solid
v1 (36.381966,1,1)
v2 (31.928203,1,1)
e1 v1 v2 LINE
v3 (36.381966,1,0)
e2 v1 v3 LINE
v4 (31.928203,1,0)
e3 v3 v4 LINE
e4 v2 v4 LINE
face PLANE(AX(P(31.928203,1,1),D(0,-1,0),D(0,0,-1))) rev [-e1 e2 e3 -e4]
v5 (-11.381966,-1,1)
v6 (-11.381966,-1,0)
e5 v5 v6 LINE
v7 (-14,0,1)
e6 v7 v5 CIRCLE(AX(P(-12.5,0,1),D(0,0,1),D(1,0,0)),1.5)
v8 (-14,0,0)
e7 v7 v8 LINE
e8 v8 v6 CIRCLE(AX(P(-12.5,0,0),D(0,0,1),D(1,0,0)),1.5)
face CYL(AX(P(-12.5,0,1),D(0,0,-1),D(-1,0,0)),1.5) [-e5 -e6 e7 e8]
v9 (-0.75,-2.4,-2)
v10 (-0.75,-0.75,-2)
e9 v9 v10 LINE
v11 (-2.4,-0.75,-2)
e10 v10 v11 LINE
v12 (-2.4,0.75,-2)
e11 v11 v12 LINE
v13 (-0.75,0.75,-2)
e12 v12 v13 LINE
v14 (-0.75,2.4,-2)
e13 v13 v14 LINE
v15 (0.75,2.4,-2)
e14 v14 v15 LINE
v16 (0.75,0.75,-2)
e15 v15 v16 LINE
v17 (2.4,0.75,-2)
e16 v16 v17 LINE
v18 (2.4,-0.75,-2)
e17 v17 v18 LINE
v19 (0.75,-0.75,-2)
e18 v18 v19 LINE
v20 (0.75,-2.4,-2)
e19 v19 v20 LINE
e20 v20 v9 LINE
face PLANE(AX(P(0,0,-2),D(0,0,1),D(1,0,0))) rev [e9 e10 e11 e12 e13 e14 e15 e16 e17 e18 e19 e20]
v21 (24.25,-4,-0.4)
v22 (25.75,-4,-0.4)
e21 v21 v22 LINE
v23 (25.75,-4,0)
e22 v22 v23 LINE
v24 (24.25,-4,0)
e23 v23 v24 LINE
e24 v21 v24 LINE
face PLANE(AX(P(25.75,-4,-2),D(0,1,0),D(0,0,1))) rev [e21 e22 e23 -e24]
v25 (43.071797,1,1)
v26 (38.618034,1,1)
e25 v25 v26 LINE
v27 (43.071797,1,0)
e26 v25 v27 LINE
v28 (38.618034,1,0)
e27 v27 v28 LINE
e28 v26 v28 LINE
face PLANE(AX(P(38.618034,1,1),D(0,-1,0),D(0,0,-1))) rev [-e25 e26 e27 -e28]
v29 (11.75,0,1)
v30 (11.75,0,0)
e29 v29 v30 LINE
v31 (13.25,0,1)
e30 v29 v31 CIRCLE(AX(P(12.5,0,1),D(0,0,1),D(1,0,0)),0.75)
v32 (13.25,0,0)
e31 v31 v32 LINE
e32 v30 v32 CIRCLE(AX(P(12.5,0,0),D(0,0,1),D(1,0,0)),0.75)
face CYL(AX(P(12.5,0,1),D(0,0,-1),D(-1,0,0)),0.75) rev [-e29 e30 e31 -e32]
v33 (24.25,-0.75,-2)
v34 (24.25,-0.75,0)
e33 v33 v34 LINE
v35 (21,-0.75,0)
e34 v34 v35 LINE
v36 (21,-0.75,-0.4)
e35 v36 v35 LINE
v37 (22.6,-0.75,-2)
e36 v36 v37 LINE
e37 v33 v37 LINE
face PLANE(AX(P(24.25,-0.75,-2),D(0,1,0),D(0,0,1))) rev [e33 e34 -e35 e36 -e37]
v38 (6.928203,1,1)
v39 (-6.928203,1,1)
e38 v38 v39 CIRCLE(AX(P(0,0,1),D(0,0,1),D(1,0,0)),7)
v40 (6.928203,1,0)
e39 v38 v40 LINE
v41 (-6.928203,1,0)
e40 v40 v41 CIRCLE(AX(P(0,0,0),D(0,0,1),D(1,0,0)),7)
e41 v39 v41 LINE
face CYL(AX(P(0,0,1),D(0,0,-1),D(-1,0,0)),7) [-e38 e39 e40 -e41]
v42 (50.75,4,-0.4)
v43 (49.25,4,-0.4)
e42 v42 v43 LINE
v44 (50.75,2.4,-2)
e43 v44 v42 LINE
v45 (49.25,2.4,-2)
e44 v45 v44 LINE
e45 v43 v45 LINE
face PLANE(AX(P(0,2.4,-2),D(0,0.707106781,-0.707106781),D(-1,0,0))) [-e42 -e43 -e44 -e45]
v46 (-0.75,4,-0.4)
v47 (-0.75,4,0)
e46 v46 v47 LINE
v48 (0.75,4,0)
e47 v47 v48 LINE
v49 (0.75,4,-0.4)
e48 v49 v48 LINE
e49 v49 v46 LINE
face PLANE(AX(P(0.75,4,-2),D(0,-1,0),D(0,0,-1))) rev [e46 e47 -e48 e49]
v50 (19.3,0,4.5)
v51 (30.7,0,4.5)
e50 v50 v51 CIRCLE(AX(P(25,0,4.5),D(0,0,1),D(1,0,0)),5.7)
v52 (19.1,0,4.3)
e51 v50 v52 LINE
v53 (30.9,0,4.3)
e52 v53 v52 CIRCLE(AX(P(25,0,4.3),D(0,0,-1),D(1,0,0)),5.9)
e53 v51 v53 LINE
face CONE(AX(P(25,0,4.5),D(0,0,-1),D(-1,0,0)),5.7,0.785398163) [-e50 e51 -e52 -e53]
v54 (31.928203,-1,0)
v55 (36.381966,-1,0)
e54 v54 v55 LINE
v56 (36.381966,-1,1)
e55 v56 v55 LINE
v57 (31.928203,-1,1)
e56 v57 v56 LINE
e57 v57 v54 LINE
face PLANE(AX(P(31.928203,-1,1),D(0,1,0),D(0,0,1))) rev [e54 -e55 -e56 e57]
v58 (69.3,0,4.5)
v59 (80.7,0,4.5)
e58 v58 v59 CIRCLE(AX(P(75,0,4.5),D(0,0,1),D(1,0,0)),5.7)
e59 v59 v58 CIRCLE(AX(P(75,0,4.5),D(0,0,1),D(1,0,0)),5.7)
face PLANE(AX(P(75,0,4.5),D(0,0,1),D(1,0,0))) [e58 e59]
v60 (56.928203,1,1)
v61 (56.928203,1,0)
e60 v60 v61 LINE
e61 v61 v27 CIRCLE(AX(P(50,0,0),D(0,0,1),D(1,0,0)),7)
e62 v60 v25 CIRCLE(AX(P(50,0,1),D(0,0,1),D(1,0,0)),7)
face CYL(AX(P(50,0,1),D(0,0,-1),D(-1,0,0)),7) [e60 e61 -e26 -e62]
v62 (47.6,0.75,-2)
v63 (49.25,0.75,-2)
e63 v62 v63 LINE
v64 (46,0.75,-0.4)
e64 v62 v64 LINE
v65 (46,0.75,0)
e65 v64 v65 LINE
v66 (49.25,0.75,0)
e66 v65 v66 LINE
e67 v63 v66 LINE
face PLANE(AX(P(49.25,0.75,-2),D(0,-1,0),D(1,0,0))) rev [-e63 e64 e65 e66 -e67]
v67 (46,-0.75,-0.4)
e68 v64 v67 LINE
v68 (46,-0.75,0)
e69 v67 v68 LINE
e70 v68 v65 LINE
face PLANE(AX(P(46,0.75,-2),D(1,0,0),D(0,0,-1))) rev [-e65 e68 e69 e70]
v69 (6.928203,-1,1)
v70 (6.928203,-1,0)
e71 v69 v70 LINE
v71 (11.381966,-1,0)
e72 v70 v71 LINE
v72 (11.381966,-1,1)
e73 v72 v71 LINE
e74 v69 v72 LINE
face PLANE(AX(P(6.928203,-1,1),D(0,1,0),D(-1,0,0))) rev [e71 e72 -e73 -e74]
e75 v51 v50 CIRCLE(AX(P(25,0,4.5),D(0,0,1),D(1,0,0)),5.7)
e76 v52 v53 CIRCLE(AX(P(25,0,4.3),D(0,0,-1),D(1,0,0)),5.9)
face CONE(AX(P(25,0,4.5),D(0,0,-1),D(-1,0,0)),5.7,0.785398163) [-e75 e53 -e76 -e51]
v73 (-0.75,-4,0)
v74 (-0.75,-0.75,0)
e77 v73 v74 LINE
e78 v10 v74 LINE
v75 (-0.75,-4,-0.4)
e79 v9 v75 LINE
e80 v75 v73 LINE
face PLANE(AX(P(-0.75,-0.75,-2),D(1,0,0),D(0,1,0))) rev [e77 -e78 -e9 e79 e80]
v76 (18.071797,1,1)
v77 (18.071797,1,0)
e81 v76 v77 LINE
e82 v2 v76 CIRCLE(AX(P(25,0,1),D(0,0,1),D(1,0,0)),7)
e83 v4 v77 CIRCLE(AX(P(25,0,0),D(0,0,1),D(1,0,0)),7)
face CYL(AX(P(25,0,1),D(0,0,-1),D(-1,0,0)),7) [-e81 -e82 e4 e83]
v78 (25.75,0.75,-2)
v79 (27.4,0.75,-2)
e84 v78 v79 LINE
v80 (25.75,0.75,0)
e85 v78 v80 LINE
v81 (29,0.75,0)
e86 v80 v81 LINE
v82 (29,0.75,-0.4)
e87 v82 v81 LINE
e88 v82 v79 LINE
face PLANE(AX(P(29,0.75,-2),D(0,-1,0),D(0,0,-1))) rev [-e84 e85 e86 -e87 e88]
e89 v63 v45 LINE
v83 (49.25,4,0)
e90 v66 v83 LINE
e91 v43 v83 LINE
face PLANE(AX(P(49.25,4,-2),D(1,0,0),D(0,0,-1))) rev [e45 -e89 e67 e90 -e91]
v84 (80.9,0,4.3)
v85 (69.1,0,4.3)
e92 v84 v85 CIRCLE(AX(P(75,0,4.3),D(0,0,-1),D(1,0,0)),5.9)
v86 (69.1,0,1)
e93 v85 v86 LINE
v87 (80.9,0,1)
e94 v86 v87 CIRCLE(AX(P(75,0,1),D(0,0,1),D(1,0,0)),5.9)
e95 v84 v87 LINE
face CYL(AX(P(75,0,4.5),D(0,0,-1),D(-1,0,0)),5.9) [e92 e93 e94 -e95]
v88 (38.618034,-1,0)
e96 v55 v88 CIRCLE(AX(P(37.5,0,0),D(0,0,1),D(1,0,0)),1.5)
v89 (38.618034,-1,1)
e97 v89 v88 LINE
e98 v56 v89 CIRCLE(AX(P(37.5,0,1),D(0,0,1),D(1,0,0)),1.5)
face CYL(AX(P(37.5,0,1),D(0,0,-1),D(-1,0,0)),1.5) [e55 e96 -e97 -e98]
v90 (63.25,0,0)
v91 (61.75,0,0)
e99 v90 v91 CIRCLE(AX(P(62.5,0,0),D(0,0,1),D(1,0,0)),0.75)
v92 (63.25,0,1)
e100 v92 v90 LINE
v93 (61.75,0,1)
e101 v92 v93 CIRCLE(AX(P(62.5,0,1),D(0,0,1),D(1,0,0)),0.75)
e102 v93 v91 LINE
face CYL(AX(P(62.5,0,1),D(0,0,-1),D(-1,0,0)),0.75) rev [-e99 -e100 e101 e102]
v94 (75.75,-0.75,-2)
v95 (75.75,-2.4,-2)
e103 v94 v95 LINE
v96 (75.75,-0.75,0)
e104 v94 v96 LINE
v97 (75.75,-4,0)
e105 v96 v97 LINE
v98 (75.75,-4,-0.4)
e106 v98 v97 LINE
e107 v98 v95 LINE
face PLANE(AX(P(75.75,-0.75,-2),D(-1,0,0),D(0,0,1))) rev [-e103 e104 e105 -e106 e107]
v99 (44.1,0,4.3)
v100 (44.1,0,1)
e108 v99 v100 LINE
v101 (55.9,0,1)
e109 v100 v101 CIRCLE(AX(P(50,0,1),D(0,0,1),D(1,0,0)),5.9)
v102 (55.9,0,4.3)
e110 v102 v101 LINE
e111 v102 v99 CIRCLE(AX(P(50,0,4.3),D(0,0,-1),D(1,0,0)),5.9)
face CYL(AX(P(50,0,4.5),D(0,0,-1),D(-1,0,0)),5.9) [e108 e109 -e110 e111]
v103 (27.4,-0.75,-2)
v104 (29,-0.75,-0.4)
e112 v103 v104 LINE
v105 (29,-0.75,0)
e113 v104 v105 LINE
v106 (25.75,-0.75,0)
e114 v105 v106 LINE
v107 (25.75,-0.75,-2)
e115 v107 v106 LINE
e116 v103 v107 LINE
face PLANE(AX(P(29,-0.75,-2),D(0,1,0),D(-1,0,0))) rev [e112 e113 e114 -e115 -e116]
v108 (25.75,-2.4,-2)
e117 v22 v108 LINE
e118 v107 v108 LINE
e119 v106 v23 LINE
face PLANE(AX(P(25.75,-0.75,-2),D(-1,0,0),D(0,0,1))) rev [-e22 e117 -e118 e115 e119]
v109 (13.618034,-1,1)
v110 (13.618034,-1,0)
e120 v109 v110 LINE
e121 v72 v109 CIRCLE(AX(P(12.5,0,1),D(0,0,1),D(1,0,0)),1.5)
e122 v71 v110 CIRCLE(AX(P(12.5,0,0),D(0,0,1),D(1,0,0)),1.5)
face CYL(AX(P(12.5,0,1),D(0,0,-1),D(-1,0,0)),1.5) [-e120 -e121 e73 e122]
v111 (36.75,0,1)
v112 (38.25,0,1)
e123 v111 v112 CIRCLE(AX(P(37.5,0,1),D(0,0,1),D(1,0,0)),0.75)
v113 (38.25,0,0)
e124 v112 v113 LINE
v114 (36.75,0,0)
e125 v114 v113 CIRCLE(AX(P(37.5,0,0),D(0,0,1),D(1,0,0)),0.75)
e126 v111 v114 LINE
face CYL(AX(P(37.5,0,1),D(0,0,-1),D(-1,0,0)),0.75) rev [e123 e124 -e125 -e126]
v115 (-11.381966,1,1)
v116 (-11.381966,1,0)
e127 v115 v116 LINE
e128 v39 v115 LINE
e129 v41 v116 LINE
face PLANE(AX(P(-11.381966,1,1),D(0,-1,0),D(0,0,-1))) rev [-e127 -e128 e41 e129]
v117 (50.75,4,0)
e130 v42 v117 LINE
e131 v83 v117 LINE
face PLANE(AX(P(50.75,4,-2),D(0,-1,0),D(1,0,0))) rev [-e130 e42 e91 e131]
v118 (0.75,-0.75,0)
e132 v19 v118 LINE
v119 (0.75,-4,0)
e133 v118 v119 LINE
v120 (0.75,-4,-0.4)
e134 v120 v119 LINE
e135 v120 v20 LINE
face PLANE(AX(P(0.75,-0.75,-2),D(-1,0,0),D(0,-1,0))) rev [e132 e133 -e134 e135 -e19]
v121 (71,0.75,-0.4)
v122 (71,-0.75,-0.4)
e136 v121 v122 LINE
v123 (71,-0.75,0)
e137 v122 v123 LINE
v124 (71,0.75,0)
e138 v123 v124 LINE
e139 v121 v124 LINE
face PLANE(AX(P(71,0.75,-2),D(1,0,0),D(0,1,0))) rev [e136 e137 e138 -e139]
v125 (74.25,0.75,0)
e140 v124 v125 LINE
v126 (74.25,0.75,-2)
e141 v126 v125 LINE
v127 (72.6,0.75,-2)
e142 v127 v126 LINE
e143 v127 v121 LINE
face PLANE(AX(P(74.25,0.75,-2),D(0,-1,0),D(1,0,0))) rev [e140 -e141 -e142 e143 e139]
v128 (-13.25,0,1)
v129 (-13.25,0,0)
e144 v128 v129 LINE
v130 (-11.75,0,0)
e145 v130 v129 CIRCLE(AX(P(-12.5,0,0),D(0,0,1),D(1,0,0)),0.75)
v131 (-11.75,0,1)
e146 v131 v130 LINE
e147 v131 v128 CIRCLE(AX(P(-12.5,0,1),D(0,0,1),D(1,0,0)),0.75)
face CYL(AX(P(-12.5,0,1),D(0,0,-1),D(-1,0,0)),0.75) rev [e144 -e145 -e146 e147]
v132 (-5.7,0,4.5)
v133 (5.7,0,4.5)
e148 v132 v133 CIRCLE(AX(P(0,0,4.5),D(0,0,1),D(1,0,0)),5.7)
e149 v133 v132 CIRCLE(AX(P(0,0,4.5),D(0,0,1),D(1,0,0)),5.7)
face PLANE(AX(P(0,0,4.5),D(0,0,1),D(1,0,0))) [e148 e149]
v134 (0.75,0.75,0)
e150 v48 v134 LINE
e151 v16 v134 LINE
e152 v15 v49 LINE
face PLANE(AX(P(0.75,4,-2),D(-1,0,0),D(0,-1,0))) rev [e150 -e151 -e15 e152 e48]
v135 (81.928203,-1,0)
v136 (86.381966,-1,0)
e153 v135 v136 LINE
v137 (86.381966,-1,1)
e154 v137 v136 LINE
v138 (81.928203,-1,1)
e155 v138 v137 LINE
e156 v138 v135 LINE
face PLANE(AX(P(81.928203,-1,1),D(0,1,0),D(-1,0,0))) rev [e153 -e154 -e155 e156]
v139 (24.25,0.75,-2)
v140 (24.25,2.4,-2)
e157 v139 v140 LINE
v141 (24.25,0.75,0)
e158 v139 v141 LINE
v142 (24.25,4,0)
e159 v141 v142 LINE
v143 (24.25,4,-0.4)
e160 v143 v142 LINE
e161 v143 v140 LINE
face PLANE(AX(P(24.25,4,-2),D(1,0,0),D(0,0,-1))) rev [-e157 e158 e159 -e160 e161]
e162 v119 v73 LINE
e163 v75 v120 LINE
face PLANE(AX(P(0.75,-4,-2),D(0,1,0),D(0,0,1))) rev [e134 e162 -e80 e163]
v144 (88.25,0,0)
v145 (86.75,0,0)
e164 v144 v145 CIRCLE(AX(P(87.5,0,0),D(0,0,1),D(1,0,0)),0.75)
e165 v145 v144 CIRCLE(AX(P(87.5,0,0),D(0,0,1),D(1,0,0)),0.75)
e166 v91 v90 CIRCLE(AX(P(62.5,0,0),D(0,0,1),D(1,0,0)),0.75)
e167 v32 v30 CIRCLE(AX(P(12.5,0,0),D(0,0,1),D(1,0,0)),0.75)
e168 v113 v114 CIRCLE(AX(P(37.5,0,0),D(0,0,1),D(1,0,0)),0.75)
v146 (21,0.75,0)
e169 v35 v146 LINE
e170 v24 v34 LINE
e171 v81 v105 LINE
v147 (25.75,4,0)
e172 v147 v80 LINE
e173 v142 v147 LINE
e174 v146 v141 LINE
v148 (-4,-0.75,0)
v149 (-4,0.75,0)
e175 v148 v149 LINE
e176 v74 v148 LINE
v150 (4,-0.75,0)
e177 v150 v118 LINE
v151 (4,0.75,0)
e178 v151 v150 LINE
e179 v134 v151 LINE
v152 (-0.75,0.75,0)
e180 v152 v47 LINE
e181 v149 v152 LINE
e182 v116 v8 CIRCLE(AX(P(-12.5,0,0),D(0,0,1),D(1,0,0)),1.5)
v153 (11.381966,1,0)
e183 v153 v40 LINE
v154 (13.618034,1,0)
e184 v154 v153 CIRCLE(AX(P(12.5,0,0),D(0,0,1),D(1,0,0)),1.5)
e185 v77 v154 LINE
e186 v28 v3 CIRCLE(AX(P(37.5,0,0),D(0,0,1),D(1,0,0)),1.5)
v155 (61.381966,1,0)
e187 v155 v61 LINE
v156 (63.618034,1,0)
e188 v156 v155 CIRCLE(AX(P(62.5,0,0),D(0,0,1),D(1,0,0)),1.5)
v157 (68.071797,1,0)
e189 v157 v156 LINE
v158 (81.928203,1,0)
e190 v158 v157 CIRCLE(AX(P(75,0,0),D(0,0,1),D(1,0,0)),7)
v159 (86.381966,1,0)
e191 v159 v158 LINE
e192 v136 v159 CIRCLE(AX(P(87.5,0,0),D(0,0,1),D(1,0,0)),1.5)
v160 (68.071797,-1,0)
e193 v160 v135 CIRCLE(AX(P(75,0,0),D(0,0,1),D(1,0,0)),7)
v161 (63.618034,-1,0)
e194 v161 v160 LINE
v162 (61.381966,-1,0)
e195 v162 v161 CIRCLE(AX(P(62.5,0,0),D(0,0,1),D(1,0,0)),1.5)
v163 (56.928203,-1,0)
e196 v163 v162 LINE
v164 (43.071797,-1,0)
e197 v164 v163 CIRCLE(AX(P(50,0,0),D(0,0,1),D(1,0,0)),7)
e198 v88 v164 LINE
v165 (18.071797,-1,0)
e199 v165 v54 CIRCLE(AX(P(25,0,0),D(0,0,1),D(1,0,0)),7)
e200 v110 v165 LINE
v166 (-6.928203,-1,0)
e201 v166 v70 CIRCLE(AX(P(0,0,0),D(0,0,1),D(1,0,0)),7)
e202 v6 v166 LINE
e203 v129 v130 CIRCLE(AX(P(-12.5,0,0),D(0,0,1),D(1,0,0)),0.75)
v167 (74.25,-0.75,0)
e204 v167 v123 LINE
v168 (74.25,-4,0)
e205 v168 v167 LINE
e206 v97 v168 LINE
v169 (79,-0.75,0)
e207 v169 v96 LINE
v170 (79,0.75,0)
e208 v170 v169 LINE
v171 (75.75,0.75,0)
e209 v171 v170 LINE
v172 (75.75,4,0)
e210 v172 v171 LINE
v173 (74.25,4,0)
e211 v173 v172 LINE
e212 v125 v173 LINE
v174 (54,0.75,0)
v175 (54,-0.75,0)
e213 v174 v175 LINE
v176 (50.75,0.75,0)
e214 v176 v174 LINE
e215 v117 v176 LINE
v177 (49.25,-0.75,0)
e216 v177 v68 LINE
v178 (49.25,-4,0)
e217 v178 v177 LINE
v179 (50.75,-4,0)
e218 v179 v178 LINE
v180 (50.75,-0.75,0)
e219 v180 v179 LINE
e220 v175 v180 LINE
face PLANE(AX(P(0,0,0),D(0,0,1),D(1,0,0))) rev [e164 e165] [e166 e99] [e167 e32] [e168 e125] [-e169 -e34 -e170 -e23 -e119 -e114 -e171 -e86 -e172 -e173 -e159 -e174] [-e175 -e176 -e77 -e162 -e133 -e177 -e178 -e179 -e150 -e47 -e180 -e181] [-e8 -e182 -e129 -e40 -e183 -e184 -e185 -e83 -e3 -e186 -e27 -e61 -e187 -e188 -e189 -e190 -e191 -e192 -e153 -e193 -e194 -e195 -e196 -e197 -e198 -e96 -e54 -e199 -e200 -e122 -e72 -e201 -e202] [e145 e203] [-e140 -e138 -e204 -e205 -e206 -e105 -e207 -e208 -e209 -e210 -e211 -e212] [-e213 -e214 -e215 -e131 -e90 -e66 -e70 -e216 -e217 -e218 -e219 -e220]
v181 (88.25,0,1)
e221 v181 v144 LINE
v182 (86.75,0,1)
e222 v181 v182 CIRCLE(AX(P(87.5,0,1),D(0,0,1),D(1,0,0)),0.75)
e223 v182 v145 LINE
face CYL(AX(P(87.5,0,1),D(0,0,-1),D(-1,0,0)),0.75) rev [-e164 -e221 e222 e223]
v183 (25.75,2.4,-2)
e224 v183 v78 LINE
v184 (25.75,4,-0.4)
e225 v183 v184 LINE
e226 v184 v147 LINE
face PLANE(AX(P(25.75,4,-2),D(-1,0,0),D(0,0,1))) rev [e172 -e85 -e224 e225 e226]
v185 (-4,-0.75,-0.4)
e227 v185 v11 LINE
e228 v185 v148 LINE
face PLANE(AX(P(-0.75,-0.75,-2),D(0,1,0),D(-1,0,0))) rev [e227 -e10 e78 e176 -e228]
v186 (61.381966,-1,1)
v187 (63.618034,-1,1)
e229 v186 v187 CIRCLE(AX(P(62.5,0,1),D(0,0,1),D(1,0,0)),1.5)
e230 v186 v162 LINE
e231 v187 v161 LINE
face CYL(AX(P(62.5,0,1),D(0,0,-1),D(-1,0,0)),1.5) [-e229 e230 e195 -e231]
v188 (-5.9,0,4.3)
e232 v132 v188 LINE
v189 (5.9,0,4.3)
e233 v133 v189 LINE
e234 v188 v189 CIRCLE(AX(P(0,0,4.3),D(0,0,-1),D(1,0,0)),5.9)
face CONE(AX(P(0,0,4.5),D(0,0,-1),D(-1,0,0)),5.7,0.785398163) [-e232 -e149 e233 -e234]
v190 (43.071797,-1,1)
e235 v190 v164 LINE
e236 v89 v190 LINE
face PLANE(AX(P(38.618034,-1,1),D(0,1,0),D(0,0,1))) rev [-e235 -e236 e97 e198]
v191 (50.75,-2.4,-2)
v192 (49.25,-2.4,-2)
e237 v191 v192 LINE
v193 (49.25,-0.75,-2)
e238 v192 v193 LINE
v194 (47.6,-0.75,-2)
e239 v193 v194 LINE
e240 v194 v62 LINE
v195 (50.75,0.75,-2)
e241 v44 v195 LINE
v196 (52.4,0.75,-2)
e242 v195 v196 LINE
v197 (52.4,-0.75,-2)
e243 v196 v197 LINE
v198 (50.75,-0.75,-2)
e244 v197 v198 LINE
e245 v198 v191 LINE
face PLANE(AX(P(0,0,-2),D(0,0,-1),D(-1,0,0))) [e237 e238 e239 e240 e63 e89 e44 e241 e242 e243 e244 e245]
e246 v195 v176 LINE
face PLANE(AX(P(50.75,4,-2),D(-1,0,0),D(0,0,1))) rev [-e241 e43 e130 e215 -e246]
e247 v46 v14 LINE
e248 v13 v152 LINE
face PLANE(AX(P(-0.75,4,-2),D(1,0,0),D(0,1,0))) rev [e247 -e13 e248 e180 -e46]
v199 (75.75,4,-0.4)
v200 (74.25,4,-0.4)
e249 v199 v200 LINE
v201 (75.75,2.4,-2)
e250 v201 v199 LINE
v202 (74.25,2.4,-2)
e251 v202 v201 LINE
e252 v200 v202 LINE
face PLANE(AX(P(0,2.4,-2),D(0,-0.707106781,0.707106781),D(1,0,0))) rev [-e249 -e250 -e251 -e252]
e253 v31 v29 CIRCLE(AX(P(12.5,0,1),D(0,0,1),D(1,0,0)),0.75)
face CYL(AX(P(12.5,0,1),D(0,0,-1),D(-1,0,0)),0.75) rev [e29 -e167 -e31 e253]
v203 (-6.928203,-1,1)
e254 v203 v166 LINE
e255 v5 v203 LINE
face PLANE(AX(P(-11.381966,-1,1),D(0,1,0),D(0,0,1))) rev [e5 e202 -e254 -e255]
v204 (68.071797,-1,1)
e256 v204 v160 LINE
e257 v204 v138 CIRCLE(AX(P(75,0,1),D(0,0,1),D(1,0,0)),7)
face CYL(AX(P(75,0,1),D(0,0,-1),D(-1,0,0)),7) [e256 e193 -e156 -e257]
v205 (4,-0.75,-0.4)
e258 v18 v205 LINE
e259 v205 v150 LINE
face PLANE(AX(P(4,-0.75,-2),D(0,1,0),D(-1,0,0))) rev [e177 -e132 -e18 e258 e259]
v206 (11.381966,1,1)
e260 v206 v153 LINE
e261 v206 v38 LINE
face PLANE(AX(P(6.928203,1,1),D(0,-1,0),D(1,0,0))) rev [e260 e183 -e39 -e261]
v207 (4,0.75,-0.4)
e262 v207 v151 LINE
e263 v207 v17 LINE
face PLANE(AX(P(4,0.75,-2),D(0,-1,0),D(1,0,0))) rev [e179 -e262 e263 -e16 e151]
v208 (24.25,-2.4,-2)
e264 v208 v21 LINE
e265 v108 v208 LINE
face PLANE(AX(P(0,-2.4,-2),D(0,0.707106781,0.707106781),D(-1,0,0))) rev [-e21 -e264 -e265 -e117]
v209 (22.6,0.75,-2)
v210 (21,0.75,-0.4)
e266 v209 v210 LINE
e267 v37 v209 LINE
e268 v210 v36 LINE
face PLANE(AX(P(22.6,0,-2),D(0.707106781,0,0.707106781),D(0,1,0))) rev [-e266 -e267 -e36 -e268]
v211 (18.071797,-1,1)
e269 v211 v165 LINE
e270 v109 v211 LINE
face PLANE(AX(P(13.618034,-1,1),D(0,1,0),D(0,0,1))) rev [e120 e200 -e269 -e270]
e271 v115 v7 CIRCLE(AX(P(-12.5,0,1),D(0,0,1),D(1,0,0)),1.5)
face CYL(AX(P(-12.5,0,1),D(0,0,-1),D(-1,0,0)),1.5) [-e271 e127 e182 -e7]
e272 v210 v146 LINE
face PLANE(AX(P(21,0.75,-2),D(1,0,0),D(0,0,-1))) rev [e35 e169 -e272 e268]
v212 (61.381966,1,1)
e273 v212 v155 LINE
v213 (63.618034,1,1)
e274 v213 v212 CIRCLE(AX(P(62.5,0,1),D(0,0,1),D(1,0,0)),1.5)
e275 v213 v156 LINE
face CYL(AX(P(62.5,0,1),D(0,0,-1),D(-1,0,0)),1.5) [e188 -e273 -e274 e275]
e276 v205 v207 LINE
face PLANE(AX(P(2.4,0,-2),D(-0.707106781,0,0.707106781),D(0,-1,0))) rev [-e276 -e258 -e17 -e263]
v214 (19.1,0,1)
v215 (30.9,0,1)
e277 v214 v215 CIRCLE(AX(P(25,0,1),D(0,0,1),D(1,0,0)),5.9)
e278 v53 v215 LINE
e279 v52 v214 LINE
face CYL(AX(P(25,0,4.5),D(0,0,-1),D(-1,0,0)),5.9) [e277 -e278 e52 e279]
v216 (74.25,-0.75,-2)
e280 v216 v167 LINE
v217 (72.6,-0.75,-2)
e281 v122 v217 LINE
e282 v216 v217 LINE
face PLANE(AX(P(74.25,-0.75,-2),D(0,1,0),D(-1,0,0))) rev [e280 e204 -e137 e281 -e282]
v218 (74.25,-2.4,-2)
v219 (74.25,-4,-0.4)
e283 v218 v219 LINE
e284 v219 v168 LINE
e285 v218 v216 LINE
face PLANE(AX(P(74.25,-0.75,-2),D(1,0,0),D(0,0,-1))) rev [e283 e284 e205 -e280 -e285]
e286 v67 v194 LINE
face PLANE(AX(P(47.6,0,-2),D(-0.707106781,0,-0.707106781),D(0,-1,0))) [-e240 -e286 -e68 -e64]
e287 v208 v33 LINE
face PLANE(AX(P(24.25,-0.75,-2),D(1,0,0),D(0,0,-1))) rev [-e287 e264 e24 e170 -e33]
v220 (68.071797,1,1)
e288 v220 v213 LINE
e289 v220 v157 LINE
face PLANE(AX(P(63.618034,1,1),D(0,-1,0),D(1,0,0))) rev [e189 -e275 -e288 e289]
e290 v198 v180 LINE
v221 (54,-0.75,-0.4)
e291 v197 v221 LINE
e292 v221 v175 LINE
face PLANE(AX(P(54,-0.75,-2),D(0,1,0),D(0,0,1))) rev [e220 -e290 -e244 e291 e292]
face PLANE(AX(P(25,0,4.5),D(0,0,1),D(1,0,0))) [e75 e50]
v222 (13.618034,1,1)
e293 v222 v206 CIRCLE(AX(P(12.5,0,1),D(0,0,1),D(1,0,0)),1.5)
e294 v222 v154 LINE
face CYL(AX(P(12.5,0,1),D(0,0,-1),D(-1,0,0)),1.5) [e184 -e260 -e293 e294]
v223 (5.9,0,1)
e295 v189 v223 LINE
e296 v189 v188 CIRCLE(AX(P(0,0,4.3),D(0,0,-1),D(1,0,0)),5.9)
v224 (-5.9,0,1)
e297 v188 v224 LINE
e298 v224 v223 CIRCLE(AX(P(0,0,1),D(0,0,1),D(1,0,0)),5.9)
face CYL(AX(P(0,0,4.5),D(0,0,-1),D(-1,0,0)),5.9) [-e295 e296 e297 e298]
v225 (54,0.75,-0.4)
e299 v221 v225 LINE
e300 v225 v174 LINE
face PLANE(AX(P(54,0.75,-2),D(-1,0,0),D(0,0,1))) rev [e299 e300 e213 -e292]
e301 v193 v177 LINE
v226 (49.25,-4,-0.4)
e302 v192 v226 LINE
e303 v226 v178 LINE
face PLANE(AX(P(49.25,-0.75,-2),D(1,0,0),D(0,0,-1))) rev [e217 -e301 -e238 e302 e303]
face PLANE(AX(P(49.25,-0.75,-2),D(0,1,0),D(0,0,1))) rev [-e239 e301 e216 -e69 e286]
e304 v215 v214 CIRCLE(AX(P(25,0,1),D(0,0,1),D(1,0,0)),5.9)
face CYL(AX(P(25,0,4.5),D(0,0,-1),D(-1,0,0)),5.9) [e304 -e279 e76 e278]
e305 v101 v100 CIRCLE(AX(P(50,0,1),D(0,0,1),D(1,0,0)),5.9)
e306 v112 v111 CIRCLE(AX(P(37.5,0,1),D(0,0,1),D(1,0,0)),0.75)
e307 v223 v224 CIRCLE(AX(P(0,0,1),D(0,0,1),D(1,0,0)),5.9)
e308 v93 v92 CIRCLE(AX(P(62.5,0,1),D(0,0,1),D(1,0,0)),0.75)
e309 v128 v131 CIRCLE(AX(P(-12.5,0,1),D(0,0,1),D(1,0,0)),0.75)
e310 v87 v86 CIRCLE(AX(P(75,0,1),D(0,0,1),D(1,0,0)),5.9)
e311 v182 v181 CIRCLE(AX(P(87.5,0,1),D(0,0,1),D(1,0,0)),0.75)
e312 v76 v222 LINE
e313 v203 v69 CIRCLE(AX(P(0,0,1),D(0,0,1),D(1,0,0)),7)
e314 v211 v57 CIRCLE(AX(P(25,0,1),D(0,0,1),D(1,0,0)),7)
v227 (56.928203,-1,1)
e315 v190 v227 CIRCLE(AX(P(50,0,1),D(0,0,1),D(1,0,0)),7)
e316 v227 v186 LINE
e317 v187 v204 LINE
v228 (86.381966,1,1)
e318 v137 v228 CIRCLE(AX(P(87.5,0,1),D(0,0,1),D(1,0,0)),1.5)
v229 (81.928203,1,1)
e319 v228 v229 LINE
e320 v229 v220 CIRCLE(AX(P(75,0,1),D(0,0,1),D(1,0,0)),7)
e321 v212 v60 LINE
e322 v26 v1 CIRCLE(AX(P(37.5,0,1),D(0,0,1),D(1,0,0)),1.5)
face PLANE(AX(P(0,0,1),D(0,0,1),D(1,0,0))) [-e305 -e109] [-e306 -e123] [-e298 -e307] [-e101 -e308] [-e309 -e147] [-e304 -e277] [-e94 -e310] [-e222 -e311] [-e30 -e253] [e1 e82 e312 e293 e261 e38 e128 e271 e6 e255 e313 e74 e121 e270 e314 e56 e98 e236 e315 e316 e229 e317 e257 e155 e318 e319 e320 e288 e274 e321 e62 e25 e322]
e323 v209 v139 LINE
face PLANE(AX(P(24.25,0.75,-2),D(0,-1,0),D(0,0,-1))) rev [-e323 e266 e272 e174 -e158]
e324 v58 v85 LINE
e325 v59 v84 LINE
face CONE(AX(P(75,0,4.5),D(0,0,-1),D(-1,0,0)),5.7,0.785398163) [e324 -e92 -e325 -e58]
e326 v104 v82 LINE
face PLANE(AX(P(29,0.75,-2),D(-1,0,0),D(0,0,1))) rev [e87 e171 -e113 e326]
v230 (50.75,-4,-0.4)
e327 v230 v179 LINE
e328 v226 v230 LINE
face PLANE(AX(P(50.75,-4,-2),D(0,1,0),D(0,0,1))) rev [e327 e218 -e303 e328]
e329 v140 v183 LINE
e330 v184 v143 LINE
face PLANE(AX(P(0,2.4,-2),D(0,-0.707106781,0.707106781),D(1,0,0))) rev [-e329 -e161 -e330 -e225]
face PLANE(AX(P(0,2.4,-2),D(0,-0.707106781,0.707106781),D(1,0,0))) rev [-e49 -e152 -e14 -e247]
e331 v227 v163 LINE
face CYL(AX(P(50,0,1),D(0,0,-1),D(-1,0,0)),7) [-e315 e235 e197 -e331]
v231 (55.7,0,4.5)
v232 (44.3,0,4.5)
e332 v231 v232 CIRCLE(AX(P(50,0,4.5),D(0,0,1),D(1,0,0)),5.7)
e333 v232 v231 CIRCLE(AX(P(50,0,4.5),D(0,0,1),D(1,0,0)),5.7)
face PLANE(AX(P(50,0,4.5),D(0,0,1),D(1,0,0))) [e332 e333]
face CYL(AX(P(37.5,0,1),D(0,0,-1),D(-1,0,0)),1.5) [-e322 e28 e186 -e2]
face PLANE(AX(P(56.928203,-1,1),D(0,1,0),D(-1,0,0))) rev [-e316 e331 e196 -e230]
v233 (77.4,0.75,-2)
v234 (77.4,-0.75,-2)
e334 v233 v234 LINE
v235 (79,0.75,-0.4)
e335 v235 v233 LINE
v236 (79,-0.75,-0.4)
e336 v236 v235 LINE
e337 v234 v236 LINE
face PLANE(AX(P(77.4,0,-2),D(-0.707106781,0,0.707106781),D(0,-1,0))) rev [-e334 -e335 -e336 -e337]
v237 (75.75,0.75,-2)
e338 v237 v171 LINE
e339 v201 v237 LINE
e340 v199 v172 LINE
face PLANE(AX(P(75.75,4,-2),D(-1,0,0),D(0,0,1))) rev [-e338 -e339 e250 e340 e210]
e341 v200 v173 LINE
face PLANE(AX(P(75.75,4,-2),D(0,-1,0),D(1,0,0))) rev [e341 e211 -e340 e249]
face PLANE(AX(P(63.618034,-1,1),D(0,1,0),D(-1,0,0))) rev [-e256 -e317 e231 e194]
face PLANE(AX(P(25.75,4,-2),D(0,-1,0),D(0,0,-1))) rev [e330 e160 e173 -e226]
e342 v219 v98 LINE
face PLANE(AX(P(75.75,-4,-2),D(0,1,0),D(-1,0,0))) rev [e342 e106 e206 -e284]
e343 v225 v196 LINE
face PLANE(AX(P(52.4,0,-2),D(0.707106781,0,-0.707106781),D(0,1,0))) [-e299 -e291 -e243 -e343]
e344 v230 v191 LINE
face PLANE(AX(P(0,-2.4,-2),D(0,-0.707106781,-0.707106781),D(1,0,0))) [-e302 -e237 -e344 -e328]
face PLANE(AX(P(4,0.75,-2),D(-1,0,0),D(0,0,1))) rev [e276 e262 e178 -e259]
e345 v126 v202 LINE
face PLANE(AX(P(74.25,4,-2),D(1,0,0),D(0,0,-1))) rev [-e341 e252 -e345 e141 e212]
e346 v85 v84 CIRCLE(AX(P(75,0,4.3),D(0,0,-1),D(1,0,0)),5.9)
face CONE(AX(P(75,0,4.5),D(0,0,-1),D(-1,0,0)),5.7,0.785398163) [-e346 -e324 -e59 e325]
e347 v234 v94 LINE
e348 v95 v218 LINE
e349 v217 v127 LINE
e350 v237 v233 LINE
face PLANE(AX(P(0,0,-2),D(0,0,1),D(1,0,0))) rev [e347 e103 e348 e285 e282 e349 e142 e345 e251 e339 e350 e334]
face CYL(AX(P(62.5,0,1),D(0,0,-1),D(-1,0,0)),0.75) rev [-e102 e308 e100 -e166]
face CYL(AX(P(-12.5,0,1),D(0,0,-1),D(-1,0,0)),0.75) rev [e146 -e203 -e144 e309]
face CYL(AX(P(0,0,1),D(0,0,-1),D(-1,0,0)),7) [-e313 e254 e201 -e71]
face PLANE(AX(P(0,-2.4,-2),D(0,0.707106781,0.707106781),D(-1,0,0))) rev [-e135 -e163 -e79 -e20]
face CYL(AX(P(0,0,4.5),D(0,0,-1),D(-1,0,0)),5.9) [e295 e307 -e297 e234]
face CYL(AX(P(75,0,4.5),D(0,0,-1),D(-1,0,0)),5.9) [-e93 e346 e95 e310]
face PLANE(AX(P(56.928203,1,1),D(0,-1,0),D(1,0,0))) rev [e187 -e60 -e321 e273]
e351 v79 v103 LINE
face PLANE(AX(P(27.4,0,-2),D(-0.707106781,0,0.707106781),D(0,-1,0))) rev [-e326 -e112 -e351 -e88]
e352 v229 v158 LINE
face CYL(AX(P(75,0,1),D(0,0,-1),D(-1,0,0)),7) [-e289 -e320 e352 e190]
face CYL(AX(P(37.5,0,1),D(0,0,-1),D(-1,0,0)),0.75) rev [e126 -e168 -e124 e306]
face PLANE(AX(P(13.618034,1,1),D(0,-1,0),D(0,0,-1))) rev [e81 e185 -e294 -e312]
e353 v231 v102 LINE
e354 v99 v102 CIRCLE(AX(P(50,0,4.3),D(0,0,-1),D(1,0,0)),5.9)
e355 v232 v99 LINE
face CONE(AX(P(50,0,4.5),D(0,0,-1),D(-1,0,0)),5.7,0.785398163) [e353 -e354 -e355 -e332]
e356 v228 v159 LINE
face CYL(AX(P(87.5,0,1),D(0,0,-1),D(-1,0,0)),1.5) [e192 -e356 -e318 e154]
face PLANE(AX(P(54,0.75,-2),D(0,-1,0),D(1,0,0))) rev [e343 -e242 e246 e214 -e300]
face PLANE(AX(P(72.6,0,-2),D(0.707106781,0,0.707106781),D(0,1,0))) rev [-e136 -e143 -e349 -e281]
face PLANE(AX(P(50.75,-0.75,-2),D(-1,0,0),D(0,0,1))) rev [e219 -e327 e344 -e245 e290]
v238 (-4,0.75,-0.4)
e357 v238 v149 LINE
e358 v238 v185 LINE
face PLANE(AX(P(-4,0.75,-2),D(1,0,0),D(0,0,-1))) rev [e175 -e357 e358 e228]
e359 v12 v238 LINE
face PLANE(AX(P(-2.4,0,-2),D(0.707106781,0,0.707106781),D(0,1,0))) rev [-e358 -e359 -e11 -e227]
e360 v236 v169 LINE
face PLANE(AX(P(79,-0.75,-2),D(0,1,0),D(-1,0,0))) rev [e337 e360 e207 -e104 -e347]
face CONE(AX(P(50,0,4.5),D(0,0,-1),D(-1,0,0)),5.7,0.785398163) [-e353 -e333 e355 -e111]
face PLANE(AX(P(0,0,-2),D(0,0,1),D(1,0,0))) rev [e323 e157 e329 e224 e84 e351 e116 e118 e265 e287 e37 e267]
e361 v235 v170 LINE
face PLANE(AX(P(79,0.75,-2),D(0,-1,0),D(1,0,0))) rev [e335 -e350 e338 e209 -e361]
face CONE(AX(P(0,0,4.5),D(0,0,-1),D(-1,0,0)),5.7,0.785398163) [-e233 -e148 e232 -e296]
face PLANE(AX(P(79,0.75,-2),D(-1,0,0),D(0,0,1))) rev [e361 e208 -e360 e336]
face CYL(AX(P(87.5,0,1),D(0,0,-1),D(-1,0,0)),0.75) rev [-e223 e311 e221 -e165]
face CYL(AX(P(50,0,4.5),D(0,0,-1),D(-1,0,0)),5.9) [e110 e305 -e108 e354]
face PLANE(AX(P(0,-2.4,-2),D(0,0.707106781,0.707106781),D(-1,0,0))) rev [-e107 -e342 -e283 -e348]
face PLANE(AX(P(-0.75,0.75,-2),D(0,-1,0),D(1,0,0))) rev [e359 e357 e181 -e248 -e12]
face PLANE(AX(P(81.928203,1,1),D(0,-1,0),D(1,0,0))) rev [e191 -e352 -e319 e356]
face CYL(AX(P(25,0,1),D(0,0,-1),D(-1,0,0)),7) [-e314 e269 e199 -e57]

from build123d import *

# Parameters (mm, degrees)
SKETCH1_R           = 0.75
BOSS_EXTRUDE1_DEPTH = 1
SKETCH2_R           = 5.9
BOSS_EXTRUDE2_DEPTH = 3.5
CHAMFER1_SIZE       = 0.2
BOSS_EXTRUDE3_DEPTH = 2
CHAMFER2_SIZE       = 1.6


with BuildPart() as part:
    # Sketch1 → Boss-Extrude1 (new body)
    with BuildSketch(Plane.XY):
        with BuildLine():
            Line((-11.381966011, 1), (-6.92820323, 1))
            ThreePointArc((-6.92820323, 1), (0, 7), (6.92820323, 1))
            Line((6.92820323, 1), (11.381966011, 1))
            ThreePointArc((11.381966011, 1), (12.5, 1.5), (13.618033989, 1))
            Line((13.618033989, 1), (18.07179677, 1))
            ThreePointArc((18.07179677, 1), (25, 7), (31.92820323, 1))
            Line((31.92820323, 1), (36.381966011, 1))
            ThreePointArc((36.381966011, 1), (37.5, 1.5), (38.618033989, 1))
            Line((38.618033989, 1), (43.07179677, 1))
            ThreePointArc((43.07179677, 1), (50, 7), (56.92820323, 1))
            Line((56.92820323, 1), (61.381966011, 1))
            ThreePointArc((61.381966011, 1), (62.5, 1.5), (63.618033989, 1))
            Line((63.618033989, 1), (68.07179677, 1))
            ThreePointArc((68.07179677, 1), (75, 7), (81.92820323, 1))
            Line((81.92820323, 1), (86.381966011, 1))
            ThreePointArc((86.381966011, 1), (89, 0), (86.381966011, -1))
            Line((86.381966011, -1), (81.92820323, -1))
            ThreePointArc((81.92820323, -1), (75, -7), (68.07179677, -1))
            Line((68.07179677, -1), (63.618033989, -1))
            ThreePointArc((63.618033989, -1), (62.5, -1.5), (61.381966011, -1))
            Line((61.381966011, -1), (56.92820323, -1))
            ThreePointArc((56.92820323, -1), (50, -7), (43.07179677, -1))
            Line((43.07179677, -1), (38.618033989, -1))
            ThreePointArc((38.618033989, -1), (37.5, -1.5), (36.381966011, -1))
            Line((36.381966011, -1), (31.92820323, -1))
            ThreePointArc((31.92820323, -1), (25, -7), (18.07179677, -1))
            Line((18.07179677, -1), (13.618033989, -1))
            ThreePointArc((13.618033989, -1), (12.5, -1.5), (11.381966011, -1))
            Line((11.381966011, -1), (6.92820323, -1))
            ThreePointArc((6.92820323, -1), (0, -7), (-6.92820323, -1))
            Line((-6.92820323, -1), (-11.381966011, -1))
            ThreePointArc((-11.381966011, -1), (-14, 0), (-11.381966011, 1))
        make_face()
        with Locations((12.5, 0)):
            Circle(SKETCH1_R, mode=Mode.SUBTRACT)
        with Locations((37.5, 0)):
            Circle(SKETCH1_R, mode=Mode.SUBTRACT)
        with Locations((62.5, 0)):
            Circle(SKETCH1_R, mode=Mode.SUBTRACT)
        with Locations((-12.5, 0)):
            Circle(SKETCH1_R, mode=Mode.SUBTRACT)
        with Locations((87.5, 0)):
            Circle(SKETCH1_R, mode=Mode.SUBTRACT)
    extrude(amount=BOSS_EXTRUDE1_DEPTH)

    # Sketch2 → Boss-Extrude2 (add)
    with BuildSketch(Plane.XY.offset(1)):
        Circle(SKETCH2_R)
        with Locations((25, 0)):
            Circle(SKETCH2_R)
        with Locations((50, 0)):
            Circle(SKETCH2_R)
        with Locations((75, 0)):
            Circle(SKETCH2_R)
    extrude(amount=BOSS_EXTRUDE2_DEPTH)

    # Chamfer1
    chamfer1_edges = [part.edges().sort_by_distance(p)[0] for p in [
        (-5.9, 0, 4.5),
        (19.1, 0, 4.5),
        (44.1, 0, 4.5),
        (69.1, 0, 4.5),
    ]]
    chamfer(chamfer1_edges, length=CHAMFER1_SIZE)

    # Sketch3 → Boss-Extrude3 (add)
    with BuildSketch(Plane(origin=(0, 0, 0), x_dir=(-1, 0, 0), z_dir=(0, 0, -1))):
        Polygon((-74.25, -0.75), (-74.25, -4), (-75.75, -4), (-75.75, -0.75), (-79, -0.75), (-79, 0.75), (-75.75, 0.75), (-75.75, 4), (-74.25, 4), (-74.25, 0.75), (-71, 0.75), (-71, -0.75), align=None)
        Polygon((-50.75, 4), (-49.25, 4), (-49.25, 0.75), (-46, 0.75), (-46, -0.75), (-49.25, -0.75), (-49.25, -4), (-50.75, -4), (-50.75, -0.75), (-54, -0.75), (-54, 0.75), (-50.75, 0.75), align=None)
        Polygon((-29, 0.75), (-25.75, 0.75), (-25.75, 4), (-24.25, 4), (-24.25, 0.75), (-21, 0.75), (-21, -0.75), (-24.25, -0.75), (-24.25, -4), (-25.75, -4), (-25.75, -0.75), (-29, -0.75), align=None)
        Polygon((-4, 0.75), (-0.75, 0.75), (-0.75, 4), (0.75, 4), (0.75, 0.75), (4, 0.75), (4, -0.75), (0.75, -0.75), (0.75, -4), (-0.75, -4), (-0.75, -0.75), (-4, -0.75), align=None)
    extrude(amount=BOSS_EXTRUDE3_DEPTH)

    # Chamfer2
    chamfer2_edges = [part.edges().sort_by_distance(p)[0] for p in [
        (75, -4, -2),
        (71, 0, -2),
        (75, 4, -2),
        (79, 0, -2),
        (46, 0, -2),
        (50, 4, -2),
        (54, 0, -2),
        (50, -4, -2),
        (21, 0, -2),
        (25, 4, -2),
        (29, 0, -2),
        (25, -4, -2),
        (-4, 0, -2),
        (0, 4, -2),
        (4, 0, -2),
        (0, -4, -2),
    ]]
    chamfer(chamfer2_edges, length=CHAMFER2_SIZE)


solid = part.part
